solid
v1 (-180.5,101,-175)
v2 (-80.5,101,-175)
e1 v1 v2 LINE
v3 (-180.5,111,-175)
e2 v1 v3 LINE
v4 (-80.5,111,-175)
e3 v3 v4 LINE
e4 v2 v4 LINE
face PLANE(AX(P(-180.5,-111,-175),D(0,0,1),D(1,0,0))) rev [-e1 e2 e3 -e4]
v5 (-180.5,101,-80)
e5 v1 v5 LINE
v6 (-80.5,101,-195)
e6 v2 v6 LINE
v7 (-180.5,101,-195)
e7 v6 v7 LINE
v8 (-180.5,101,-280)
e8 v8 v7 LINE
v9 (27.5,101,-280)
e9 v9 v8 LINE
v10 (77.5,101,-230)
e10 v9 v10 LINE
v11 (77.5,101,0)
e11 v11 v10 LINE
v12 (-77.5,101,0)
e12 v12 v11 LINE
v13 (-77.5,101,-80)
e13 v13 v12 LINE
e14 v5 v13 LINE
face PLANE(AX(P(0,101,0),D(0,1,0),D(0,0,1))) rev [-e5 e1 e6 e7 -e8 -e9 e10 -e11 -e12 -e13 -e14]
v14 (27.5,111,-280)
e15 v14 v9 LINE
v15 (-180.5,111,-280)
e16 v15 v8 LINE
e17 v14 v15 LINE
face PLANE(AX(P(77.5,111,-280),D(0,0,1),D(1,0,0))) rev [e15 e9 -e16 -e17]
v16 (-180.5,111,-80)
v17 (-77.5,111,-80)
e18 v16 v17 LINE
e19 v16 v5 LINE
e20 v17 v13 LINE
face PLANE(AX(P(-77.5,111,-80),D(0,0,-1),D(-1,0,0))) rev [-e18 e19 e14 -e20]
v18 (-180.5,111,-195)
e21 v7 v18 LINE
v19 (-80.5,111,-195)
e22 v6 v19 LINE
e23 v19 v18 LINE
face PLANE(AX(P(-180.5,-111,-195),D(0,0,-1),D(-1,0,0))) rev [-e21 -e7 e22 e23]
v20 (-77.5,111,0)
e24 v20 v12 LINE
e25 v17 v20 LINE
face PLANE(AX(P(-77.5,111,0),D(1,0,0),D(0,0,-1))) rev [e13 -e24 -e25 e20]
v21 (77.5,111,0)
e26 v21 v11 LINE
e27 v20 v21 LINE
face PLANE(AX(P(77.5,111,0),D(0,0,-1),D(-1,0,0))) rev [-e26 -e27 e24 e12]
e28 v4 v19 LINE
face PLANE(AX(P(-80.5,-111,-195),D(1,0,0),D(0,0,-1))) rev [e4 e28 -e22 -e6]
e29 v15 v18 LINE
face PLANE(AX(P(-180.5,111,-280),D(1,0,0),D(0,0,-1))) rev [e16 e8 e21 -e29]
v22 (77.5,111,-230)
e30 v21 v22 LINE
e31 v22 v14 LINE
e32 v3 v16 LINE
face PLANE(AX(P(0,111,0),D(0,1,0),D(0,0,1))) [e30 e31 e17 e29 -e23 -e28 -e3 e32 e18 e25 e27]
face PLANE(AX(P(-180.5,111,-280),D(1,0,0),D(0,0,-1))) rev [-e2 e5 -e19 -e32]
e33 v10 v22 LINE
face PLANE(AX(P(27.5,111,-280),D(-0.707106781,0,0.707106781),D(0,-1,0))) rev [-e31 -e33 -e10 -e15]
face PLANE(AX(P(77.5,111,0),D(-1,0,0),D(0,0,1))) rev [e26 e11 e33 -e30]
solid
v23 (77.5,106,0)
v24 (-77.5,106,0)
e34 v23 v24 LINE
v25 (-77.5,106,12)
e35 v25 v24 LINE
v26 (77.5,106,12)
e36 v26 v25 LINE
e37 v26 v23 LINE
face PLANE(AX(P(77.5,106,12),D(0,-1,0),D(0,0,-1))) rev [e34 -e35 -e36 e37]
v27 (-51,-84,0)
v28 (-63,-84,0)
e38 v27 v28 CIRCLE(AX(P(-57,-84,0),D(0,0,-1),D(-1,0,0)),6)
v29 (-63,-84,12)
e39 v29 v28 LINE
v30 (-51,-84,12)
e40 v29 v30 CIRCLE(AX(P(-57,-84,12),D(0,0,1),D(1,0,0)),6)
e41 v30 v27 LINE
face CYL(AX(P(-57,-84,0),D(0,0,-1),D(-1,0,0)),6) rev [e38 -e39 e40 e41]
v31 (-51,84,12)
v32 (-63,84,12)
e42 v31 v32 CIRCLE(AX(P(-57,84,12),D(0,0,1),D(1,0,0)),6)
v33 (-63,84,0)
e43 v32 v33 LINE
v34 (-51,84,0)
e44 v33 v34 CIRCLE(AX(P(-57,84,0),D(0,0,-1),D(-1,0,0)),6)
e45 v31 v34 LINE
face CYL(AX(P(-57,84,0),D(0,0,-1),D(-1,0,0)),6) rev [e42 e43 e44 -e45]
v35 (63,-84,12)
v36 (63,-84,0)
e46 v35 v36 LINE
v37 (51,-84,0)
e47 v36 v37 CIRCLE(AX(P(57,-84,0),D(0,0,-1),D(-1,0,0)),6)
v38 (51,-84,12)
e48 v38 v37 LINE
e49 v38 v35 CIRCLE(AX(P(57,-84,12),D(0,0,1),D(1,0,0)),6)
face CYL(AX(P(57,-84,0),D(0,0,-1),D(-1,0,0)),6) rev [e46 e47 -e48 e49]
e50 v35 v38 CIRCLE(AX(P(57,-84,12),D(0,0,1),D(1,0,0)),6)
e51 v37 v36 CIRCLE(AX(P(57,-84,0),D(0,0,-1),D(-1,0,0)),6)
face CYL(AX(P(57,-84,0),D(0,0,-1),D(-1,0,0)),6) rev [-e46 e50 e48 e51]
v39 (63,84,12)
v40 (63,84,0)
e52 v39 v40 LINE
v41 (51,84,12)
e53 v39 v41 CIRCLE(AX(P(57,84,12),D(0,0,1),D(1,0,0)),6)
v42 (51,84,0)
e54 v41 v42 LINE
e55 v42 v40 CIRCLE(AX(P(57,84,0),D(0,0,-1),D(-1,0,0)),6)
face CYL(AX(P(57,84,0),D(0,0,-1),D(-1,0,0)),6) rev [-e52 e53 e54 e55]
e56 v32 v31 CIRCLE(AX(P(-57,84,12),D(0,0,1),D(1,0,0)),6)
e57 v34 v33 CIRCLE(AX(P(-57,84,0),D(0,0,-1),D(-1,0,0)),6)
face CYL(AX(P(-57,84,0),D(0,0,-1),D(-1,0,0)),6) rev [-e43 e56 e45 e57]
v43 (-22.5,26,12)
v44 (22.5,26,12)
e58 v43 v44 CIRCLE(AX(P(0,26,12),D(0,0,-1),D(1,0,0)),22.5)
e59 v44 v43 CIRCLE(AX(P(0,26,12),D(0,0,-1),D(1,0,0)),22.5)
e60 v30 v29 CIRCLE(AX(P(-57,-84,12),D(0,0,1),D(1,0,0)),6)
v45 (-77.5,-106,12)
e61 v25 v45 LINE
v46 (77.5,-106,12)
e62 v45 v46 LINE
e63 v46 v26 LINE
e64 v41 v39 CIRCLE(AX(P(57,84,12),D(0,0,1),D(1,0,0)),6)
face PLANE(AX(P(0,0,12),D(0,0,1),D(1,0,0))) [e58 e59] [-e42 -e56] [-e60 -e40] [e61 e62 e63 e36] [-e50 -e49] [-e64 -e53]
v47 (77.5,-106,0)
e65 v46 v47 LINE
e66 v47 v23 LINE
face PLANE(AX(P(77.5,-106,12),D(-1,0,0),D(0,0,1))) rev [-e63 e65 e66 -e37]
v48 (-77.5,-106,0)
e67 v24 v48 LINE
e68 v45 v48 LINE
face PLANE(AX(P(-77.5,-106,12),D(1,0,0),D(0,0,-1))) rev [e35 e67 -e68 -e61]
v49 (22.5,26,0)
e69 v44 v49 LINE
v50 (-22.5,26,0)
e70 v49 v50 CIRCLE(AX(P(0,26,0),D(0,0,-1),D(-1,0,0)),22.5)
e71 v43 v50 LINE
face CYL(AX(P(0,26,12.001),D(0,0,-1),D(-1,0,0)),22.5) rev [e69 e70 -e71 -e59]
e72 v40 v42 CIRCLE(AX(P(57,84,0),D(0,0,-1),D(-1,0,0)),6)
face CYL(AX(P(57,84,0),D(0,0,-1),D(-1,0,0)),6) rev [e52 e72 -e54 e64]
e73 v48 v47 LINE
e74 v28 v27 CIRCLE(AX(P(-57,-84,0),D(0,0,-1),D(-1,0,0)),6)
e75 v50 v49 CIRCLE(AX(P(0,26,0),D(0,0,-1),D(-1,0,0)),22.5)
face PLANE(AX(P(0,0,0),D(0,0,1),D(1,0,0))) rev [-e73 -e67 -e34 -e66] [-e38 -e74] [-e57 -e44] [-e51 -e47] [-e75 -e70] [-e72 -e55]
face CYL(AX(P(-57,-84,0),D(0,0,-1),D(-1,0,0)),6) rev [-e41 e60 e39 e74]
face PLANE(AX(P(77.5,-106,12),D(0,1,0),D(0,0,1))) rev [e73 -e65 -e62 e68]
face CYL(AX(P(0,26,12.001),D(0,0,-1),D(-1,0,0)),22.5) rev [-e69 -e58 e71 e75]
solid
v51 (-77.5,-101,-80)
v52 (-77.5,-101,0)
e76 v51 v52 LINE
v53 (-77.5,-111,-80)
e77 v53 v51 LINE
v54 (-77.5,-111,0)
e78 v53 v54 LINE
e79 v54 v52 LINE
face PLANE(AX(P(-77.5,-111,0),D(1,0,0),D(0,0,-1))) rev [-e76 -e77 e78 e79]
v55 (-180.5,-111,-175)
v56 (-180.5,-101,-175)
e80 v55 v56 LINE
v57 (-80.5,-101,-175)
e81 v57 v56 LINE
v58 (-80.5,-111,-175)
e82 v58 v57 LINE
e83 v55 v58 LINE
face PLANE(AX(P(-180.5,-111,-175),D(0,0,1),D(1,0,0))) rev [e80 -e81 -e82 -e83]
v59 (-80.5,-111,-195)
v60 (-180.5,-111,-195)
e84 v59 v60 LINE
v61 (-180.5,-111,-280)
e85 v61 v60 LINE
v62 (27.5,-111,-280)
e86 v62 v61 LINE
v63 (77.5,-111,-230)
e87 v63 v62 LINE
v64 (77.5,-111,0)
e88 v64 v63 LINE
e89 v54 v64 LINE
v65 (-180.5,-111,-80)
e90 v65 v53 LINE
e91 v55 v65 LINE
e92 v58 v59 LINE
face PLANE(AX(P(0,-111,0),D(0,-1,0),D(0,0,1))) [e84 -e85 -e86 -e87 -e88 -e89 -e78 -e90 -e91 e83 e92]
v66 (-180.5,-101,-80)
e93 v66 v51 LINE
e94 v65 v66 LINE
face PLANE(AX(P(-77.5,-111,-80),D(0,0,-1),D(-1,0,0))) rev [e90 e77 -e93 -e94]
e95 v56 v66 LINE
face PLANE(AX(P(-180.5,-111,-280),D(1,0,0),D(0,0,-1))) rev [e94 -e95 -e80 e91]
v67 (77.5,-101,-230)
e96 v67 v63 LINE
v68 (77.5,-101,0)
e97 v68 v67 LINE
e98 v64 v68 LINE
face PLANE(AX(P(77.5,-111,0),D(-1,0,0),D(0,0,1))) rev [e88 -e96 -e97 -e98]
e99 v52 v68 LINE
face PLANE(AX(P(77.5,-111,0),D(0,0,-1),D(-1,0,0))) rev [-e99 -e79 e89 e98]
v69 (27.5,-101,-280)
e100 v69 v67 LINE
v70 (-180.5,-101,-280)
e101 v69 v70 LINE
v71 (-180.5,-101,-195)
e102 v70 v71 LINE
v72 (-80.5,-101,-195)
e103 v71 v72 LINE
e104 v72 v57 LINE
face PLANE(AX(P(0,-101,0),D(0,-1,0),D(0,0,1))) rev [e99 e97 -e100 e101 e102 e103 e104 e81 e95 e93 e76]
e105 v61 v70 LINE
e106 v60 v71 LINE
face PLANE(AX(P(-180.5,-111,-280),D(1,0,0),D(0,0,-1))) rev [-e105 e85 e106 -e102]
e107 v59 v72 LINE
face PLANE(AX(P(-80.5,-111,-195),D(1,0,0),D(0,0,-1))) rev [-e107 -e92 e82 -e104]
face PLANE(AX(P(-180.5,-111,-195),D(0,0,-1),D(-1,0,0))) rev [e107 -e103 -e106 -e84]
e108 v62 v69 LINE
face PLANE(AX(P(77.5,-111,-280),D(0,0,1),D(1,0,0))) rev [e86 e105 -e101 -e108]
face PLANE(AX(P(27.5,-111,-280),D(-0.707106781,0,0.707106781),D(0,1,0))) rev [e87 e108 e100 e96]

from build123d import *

# Parameters (mm, degrees)
SKETCH1_W           = 155
SKETCH1_H           = 212
BOSS_EXTRUDE1_DEPTH = 12
F_12_0_12_HOLE1_D   = 12
BOSS_EXTRUDE2_DEPTH = 5
CHAMFER1_SIZE       = 50
SKETCH9_R           = 22.5
CUT_EXTRUDE1_DEPTH  = 12
SKETCH10_W          = 100
SKETCH10_H          = 20
CUT_EXTRUDE2_DEPTH  = 401.33017623


with BuildPart() as part:
    # Sketch1 → Boss-Extrude1 (new body)
    with BuildSketch(Plane.XY):
        Rectangle(SKETCH1_W, SKETCH1_H)
    extrude(amount=BOSS_EXTRUDE1_DEPTH)

    # Ø12.0 (12) Hole1 (through all)
    with Locations(Plane(origin=(0, 0, 0), x_dir=(-1, 0, 0), z_dir=(0, 0, -1))):
        with Locations((-57, 84), (57, 84), (-57, -84), (57, -84)):
            Hole(F_12_0_12_HOLE1_D / 2)

    # Sketch9 → Cut-Extrude1 (cut)
    with BuildSketch(Plane(origin=(0, 0, 0), x_dir=(-1, 0, 0), z_dir=(0, 0, -1))):
        with Locations((0, 26)):
            Circle(SKETCH9_R)
    extrude(amount=-CUT_EXTRUDE1_DEPTH, mode=Mode.SUBTRACT)


with BuildPart() as body_2:
    # Sketch8 → Boss-Extrude2 (new, symmetric)
    with BuildSketch(Plane(origin=(0, 106, 0), x_dir=(1, 0, 0), z_dir=(0, 1, 0))):
        Polygon((77.5, 0), (-77.5, 0), (-77.5, 80), (-180.5, 80), (-180.5, 280), (77.5, 280), align=None)
    extrude(amount=BOSS_EXTRUDE2_DEPTH, both=True)

    # Chamfer1
    chamfer1_edges = [body_2.edges().sort_by_distance(p)[0] for p in [
        (77.5, 106, -280),
    ]]
    chamfer(chamfer1_edges, length=CHAMFER1_SIZE)


with BuildPart() as body_3:
    # Mirror1: mirrored copy
    add(body_2.part.mirror(Plane.ZX))


with BuildPart() as cut_extrude2_tool:
    # Sketch10 → Cut-Extrude2 (new, through all)
    with BuildSketch(Plane(origin=(0, 111, 0), x_dir=(1, 0, 0), z_dir=(0, 1, 0))):
        with Locations((-130.5, 185)):
            Rectangle(SKETCH10_W, SKETCH10_H)
    extrude(amount=-CUT_EXTRUDE2_DEPTH)


with BuildPart() as body_2_1:
    add(body_2.part)

    # Cut-Extrude2: cut by cut_extrude2_tool
    add(cut_extrude2_tool.part, mode=Mode.SUBTRACT)


with BuildPart() as body_3_1:
    add(body_3.part)

    # Cut-Extrude2: cut by cut_extrude2_tool
    add(cut_extrude2_tool.part, mode=Mode.SUBTRACT)


solid = Compound([part.part, body_2_1.part, body_3_1.part])
